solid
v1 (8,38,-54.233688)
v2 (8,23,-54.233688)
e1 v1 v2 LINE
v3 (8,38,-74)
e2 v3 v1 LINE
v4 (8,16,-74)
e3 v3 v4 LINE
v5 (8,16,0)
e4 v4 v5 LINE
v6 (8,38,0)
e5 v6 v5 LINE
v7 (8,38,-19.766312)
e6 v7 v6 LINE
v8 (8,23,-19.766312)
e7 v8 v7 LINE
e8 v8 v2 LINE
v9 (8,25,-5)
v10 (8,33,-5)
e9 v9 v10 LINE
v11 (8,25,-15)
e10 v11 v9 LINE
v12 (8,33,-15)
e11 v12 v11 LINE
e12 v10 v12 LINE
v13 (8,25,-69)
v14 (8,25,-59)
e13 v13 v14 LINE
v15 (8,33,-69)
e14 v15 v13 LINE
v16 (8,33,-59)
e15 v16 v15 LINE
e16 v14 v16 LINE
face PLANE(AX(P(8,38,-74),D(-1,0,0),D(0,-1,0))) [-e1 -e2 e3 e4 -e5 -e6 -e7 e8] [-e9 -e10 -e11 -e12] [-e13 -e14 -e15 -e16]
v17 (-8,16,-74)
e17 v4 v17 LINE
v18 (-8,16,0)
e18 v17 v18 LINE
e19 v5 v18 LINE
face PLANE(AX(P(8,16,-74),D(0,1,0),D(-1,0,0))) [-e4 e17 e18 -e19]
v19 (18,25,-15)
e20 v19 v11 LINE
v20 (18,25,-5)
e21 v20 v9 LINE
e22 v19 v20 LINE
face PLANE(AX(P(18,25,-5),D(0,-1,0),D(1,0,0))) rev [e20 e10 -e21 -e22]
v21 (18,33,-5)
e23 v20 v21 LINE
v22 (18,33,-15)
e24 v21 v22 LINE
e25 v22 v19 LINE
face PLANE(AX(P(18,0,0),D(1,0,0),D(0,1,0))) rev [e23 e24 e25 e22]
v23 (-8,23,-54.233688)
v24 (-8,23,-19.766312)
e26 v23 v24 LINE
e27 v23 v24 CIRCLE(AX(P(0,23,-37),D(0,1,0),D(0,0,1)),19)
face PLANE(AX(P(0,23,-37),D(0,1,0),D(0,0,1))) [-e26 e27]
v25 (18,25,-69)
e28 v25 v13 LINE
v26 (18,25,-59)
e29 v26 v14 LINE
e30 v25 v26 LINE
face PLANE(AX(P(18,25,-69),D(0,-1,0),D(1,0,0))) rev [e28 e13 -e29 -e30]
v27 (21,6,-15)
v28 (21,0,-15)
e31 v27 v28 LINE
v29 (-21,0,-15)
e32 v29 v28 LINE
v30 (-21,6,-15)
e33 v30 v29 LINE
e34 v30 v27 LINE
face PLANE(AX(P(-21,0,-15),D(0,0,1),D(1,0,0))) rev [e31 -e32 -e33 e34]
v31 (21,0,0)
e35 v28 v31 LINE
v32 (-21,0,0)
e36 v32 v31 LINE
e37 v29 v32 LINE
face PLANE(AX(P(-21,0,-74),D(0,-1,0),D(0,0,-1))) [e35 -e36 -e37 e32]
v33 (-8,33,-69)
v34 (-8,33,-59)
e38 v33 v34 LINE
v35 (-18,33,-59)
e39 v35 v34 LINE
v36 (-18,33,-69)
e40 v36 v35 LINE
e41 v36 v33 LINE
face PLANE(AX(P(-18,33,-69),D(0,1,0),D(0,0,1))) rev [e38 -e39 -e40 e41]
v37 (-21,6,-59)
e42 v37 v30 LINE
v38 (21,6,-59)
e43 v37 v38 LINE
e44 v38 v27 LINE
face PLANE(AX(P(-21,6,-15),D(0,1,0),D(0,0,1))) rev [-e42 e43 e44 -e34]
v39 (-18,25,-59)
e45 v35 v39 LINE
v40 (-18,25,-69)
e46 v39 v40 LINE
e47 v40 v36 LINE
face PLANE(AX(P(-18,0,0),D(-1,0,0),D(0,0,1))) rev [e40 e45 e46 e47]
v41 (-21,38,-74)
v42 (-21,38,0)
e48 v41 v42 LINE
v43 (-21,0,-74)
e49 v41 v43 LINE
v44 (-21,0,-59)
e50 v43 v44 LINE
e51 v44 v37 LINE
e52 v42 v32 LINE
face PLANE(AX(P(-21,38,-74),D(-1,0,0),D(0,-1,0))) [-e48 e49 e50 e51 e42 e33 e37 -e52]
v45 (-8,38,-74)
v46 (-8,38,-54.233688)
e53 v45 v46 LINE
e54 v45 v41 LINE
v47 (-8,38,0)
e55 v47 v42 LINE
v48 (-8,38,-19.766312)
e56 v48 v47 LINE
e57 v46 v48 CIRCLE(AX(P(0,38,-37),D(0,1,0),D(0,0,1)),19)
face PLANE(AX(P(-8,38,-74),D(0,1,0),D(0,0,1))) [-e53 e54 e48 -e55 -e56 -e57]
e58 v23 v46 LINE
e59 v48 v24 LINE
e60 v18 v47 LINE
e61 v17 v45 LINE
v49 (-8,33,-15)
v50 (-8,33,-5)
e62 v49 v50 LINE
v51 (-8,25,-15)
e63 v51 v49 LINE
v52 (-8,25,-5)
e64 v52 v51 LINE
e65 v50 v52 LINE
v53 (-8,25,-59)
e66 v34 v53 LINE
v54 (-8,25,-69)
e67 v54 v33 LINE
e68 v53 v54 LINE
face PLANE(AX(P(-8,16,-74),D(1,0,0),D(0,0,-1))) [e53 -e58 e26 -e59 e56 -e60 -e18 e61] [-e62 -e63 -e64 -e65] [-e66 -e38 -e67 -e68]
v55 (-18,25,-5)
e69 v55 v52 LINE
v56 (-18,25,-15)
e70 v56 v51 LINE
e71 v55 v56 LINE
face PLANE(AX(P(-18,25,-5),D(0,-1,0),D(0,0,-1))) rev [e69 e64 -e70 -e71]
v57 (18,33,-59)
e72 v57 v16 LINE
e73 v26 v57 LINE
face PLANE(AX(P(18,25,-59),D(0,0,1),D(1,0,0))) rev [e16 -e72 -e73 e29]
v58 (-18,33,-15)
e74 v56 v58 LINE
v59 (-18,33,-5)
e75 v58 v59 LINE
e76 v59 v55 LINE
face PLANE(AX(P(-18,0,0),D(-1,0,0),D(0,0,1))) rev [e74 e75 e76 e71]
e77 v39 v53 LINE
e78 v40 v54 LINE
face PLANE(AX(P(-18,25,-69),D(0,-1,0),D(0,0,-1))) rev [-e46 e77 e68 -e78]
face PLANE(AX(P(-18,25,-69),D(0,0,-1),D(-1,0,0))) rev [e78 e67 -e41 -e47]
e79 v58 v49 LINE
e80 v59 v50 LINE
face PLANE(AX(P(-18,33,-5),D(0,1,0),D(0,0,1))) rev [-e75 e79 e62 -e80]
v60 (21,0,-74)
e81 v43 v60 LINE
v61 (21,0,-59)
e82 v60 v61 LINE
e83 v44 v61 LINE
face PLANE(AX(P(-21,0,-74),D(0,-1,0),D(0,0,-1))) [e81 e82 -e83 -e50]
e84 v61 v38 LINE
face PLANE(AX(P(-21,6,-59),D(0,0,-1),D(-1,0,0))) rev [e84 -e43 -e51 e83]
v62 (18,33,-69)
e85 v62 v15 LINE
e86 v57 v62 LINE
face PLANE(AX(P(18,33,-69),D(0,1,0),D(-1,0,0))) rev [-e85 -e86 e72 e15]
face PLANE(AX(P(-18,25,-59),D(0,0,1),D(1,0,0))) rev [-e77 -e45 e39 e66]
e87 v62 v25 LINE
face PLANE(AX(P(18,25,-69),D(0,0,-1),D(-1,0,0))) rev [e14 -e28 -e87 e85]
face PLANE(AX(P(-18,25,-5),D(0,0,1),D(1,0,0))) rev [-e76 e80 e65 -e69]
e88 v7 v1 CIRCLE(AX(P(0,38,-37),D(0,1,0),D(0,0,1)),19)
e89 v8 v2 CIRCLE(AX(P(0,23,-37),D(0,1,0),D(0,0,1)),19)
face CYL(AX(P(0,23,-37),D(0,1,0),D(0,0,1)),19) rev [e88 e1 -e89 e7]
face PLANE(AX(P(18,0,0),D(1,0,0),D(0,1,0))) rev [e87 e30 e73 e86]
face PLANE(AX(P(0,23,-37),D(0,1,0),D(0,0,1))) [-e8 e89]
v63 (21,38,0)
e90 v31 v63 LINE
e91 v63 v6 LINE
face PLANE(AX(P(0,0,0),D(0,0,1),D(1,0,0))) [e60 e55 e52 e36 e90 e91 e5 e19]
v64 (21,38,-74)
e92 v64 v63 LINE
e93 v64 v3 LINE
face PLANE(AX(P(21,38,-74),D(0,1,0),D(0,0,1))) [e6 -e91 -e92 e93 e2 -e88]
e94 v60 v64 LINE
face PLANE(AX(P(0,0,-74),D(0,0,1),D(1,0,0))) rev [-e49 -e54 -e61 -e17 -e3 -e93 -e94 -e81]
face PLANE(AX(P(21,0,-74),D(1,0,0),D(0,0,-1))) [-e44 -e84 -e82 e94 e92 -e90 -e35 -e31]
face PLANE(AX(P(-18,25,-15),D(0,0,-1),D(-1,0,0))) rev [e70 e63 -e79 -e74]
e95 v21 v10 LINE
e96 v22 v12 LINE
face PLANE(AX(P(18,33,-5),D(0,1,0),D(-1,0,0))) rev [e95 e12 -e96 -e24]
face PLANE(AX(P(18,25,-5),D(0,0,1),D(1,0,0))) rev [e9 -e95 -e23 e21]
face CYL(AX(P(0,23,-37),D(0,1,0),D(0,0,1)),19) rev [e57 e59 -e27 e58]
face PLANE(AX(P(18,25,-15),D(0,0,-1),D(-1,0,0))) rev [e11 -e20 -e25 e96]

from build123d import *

# Parameters (mm, degrees)
BLOCK_BODY_DEPTH          = 74
BASE_GROOVE_SKETCH_W      = 44
BASE_GROOVE_SKETCH_H      = 6
BASE_GROOVE_44X6_DEPTH    = 94.187982058
BORE_SKETCH_R             = 19
BORE_38_DEPTH             = 15
WALL_WINDOWS_A_SKETCH_W   = 10
WALL_WINDOWS_A_SKETCH_H   = 8
WALL_WINDOWS_A_10X8_DEPTH = 10
WALL_WINDOWS_B_SKETCH_W   = 10
WALL_WINDOWS_B_SKETCH_H   = 8
WALL_WINDOWS_B_10X8_DEPTH = 10


with BuildPart() as part:
    # Block Profile Sketch → Block Body (new body)
    with BuildSketch(Plane.XY):
        Polygon((-21, 0), (21, 0), (21, 38), (8, 38), (8, 16), (-8, 16), (-8, 38), (-21, 38), align=None)
    extrude(amount=-BLOCK_BODY_DEPTH)

    # Base Groove Sketch → Base Groove 44x6 (cut, through all)
    with BuildSketch(Plane(origin=(21, 0, 0), x_dir=(0, 0, -1), z_dir=(1, 0, 0))):
        with Locations((37, 3)):
            Rectangle(BASE_GROOVE_SKETCH_W, BASE_GROOVE_SKETCH_H)
    extrude(amount=-BASE_GROOVE_44X6_DEPTH, mode=Mode.SUBTRACT)

    # Bore Sketch → Bore Ø38 (cut)
    with BuildSketch(Plane(origin=(0, 38, 0), x_dir=(1, 0, 0), z_dir=(0, 1, 0))):
        with Locations((0, 37)):
            Circle(BORE_SKETCH_R)
    extrude(amount=-BORE_38_DEPTH, mode=Mode.SUBTRACT)

    # Wall Windows A Sketch → Wall Windows A 10x8 (cut)
    with BuildSketch(Plane(origin=(-8, 0, 0), x_dir=(0, 0, -1), z_dir=(1, 0, 0))):
        with Locations((10, 29)):
            Rectangle(WALL_WINDOWS_A_SKETCH_W, WALL_WINDOWS_A_SKETCH_H)
        with Locations((64, 29)):
            Rectangle(WALL_WINDOWS_A_SKETCH_W, WALL_WINDOWS_A_SKETCH_H)
    extrude(amount=-WALL_WINDOWS_A_10X8_DEPTH, mode=Mode.SUBTRACT)

    # Wall Windows B Sketch → Wall Windows B 10x8 (cut)
    with BuildSketch(Plane.ZY.offset(-8)):
        with Locations((-64, 29)):
            Rectangle(WALL_WINDOWS_B_SKETCH_W, WALL_WINDOWS_B_SKETCH_H)
        with Locations((-10, 29)):
            Rectangle(WALL_WINDOWS_B_SKETCH_W, WALL_WINDOWS_B_SKETCH_H)
    extrude(amount=-WALL_WINDOWS_B_10X8_DEPTH, mode=Mode.SUBTRACT)


solid = part.part
